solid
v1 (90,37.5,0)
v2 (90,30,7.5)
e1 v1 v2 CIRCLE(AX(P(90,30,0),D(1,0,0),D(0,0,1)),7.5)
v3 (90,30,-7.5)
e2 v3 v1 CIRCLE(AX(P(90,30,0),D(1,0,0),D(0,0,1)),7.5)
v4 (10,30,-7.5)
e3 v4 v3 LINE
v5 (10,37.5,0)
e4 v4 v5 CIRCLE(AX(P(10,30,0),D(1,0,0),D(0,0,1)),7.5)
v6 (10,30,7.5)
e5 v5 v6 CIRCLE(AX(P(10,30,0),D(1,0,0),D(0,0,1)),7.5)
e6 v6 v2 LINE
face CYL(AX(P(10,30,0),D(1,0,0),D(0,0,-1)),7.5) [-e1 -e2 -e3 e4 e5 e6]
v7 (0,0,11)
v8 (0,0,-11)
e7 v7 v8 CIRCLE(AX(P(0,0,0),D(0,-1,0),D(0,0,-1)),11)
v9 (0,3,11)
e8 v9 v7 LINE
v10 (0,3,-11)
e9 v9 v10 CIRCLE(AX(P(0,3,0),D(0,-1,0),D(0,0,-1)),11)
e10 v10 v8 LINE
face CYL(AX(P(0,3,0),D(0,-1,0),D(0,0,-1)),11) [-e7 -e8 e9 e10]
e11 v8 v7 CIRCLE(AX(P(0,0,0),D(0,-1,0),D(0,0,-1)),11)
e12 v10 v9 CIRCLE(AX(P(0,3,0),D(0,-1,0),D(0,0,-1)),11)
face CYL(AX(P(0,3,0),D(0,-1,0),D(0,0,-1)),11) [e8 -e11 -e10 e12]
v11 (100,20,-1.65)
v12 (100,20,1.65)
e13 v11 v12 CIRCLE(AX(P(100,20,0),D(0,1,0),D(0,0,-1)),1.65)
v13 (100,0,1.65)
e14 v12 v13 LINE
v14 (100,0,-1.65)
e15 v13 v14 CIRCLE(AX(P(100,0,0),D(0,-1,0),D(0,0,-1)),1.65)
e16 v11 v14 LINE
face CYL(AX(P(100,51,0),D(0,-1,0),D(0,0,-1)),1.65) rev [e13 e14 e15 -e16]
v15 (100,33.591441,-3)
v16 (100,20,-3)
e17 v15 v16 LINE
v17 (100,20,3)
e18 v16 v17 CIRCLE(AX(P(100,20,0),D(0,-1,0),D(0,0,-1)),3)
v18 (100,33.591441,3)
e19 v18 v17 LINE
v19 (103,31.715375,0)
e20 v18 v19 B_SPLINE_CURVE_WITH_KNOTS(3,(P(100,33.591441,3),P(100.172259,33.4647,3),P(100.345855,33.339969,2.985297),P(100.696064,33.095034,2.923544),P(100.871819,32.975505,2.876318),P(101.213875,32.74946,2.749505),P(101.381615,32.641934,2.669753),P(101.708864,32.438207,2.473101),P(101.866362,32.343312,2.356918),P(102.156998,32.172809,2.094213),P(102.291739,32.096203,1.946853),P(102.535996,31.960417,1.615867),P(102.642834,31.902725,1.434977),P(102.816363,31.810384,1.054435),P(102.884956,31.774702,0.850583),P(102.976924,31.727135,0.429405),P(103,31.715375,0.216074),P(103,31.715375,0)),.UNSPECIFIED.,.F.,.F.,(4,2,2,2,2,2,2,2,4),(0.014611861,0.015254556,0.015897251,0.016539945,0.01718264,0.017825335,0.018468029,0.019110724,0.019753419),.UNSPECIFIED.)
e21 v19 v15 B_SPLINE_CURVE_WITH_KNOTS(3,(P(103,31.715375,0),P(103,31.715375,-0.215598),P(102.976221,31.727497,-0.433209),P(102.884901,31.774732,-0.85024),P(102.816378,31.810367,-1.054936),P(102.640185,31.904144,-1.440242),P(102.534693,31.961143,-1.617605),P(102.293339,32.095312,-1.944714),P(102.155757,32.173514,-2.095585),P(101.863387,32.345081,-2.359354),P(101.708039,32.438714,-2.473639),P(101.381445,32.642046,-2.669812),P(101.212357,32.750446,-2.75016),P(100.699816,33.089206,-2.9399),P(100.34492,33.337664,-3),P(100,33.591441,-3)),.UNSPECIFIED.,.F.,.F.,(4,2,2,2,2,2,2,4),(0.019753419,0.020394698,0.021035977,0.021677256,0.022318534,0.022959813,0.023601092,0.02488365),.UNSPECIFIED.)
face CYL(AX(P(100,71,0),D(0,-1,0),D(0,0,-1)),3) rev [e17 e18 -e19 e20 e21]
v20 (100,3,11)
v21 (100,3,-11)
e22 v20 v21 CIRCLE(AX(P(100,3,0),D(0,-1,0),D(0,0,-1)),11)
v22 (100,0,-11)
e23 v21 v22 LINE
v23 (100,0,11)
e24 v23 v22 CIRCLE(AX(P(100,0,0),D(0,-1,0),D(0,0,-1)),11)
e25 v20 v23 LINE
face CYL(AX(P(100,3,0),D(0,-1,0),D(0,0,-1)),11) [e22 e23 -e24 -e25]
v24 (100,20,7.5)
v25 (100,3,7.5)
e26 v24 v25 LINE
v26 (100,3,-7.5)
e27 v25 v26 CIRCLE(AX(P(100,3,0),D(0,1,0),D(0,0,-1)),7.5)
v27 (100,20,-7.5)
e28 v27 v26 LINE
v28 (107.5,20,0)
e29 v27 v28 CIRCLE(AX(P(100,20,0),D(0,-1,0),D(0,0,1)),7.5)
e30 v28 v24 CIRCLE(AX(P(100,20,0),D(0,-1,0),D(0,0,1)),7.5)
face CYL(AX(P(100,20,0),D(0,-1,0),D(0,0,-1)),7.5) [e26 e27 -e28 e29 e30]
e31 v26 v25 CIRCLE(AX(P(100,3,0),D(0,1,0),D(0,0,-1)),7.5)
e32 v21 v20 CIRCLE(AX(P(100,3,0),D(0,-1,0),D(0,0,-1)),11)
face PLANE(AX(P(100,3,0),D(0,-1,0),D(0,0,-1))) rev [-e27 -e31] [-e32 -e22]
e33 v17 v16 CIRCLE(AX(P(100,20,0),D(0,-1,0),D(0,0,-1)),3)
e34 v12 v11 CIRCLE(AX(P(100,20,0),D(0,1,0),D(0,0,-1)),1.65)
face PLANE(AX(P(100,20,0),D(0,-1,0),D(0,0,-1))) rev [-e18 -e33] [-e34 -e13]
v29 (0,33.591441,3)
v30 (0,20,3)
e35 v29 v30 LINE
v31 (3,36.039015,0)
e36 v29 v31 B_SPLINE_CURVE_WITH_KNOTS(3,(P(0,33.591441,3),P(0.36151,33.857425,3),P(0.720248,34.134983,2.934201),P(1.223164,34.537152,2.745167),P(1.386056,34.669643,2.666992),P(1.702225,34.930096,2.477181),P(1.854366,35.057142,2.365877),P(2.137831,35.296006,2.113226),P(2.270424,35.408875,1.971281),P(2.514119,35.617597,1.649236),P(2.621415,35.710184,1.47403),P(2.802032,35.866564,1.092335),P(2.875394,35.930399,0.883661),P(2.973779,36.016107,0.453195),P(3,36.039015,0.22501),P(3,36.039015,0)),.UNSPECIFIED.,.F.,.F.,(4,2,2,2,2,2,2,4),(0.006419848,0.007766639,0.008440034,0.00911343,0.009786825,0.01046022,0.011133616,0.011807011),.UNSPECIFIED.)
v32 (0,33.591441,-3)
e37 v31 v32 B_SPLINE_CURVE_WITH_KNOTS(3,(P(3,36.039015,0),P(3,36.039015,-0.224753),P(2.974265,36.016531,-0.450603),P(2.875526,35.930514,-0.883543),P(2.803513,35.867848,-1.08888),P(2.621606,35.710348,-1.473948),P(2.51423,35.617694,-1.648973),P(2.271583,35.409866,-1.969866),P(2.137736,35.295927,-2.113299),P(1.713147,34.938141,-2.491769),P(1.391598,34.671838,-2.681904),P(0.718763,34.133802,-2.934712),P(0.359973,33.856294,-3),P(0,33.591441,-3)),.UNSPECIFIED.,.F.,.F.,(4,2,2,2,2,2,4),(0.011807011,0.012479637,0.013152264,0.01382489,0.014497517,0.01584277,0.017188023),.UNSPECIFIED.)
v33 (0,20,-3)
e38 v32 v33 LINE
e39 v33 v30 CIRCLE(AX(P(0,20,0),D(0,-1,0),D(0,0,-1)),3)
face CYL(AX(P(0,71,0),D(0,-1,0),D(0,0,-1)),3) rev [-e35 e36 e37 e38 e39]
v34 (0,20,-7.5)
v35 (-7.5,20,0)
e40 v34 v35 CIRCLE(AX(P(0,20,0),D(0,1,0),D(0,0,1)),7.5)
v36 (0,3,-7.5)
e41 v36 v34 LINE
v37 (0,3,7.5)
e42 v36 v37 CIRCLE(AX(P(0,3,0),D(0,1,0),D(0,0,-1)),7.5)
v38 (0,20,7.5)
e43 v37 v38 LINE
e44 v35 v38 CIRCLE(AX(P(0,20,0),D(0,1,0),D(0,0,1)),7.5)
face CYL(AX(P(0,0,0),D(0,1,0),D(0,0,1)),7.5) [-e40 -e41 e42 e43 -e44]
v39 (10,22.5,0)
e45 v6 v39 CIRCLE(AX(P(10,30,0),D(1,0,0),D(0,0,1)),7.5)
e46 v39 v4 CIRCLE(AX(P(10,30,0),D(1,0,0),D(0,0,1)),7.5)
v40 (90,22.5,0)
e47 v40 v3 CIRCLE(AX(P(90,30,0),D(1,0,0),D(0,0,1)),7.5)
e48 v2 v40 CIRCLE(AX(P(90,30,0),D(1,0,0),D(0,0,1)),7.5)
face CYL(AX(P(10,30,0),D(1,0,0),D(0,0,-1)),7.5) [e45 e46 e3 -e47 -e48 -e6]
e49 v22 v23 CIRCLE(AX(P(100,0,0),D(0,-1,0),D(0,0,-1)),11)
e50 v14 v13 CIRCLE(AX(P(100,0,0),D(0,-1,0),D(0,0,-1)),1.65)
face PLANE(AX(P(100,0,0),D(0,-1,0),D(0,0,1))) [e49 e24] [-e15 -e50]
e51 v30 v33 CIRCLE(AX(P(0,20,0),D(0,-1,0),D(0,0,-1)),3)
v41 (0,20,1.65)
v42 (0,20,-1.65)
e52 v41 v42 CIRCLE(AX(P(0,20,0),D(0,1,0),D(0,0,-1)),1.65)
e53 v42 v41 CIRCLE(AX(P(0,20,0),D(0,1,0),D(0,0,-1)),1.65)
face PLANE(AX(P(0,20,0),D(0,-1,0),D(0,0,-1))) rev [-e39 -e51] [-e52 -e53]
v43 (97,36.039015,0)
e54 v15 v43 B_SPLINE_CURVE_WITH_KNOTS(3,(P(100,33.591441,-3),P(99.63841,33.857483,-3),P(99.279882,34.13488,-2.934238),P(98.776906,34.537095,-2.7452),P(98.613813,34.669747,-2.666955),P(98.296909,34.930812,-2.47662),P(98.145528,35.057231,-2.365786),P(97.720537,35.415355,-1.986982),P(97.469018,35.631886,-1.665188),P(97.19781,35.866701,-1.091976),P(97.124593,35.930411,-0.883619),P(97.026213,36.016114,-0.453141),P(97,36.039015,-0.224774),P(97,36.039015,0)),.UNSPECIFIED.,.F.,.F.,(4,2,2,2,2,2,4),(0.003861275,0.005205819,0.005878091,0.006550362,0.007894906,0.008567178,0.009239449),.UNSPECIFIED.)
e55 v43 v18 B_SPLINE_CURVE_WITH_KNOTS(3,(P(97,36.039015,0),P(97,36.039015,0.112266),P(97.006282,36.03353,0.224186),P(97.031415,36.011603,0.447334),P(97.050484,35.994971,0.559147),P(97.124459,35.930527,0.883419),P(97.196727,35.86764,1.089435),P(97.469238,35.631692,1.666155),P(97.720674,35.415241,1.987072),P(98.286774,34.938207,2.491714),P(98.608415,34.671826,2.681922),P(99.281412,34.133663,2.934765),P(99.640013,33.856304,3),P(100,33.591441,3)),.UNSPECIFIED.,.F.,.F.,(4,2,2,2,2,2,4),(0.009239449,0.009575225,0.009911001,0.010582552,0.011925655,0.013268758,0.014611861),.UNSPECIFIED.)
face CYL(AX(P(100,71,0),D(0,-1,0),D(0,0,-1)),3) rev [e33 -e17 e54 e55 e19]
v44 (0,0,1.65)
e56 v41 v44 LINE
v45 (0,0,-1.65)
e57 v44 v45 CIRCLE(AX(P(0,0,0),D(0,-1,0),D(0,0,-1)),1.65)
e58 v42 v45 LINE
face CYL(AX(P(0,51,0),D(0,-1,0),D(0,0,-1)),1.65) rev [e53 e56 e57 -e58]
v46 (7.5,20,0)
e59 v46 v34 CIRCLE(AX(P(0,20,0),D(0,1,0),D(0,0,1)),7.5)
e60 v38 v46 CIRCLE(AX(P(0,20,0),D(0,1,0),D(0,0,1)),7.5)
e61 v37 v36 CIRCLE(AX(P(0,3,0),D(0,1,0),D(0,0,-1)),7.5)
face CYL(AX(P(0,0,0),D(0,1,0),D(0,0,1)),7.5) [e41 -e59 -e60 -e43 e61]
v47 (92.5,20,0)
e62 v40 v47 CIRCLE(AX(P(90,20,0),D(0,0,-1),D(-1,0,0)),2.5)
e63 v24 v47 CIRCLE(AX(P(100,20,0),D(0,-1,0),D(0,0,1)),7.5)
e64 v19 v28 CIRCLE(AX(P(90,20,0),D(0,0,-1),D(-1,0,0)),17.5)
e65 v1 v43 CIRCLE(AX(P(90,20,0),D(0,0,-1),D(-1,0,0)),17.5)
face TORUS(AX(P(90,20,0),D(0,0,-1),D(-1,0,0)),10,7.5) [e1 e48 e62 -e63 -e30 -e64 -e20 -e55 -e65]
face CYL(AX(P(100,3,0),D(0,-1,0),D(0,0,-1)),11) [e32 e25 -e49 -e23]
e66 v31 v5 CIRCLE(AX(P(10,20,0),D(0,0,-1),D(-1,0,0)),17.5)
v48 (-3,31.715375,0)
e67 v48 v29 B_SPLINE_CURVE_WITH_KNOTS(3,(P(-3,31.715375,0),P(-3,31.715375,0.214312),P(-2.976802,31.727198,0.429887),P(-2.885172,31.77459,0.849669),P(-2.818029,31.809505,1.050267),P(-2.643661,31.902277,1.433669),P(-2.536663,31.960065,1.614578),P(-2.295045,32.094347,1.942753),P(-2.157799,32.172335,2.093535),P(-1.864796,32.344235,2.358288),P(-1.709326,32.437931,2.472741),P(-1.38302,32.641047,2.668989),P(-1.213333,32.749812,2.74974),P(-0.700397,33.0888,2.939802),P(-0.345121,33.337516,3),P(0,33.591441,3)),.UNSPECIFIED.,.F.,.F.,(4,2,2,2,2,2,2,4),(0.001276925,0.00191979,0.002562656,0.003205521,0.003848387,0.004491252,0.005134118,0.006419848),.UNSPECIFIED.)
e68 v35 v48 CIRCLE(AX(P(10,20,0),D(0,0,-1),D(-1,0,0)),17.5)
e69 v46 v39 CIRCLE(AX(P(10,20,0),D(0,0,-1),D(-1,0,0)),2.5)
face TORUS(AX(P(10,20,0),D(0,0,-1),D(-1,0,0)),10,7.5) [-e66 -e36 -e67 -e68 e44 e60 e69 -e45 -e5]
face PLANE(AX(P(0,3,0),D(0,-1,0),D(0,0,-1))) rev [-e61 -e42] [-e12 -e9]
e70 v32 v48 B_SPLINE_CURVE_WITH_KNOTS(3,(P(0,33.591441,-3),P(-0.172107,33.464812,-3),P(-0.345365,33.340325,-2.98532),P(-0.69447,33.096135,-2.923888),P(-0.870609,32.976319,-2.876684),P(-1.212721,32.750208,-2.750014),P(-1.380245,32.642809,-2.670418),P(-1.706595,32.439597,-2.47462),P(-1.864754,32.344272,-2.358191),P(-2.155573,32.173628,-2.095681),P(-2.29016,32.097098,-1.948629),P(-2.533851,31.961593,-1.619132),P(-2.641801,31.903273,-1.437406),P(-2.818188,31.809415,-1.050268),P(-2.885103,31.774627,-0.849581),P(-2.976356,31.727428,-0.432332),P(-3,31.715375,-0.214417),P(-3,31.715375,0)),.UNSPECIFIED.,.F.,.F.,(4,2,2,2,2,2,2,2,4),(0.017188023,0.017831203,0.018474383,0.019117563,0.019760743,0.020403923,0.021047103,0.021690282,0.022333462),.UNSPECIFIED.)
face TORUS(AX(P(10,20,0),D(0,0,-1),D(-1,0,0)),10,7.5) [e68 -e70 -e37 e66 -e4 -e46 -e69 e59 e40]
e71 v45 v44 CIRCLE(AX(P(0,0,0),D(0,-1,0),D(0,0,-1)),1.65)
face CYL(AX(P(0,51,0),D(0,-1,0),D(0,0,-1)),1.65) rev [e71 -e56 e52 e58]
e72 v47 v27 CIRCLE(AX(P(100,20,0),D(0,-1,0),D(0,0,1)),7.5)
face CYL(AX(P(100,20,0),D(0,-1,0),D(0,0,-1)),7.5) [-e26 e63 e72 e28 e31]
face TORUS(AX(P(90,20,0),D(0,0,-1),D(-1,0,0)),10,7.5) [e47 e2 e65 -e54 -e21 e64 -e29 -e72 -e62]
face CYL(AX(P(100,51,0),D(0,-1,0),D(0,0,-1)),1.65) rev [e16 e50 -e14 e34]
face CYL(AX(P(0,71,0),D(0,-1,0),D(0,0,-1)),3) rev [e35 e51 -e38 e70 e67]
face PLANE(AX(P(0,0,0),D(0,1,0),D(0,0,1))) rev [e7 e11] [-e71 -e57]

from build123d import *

# Parameters (mm, degrees)
SKETCH_2_R          = 7.5
SKETCH_3_R          = 11
EXTRUDE_1_DEPTH     = 3
SKETCH_4_R          = 1.65
CUT_EXTRUDE_1_DEPTH = 51
CUT_EXTRUDE_START   = -20
SKETCH_5_R          = 3
CUT_EXTRUDE_2_DEPTH = 51


with BuildPart() as part:
    # 扫描1: sweep along a path in 草图1
    with BuildLine(Plane.XY) as sweep_1_path:
        Line((0, 0), (0, 20))
        ThreePointArc((0, 20), (2.928932188, 27.071067812), (10, 30))
        Line((10, 30), (90, 30))
        ThreePointArc((90, 30), (97.071067812, 27.071067812), (100, 20))
        Line((100, 20), (100, 0))
    # 草图2 → 扫描1 (sweep)
    with BuildSketch(Plane(origin=(0, 0, 0), x_dir=(1, 0, 0), z_dir=(0, 1, 0))):
        Circle(SKETCH_2_R)
    sweep(path=sweep_1_path.line)

    # 草图3 → 凸台-拉伸1 (add)
    with BuildSketch(Plane.XZ):
        with Locations(Location((0, 0, 0), (0, 0, 270))):
            Circle(SKETCH_3_R)
        with Locations(Location((100, 0, 0), (0, 0, 270))):
            Circle(SKETCH_3_R)
    extrude(amount=-EXTRUDE_1_DEPTH)

    # 草图4 → 切除-拉伸1 (cut)
    with BuildSketch(Plane.XZ):
        with Locations(Location((0, 0, 0), (0, 0, 270))):
            Circle(SKETCH_4_R)
        with Locations(Location((100, 0, 0), (0, 0, 270))):
            Circle(SKETCH_4_R)
    extrude(amount=-CUT_EXTRUDE_1_DEPTH, mode=Mode.SUBTRACT)

    # 草图5 → 切除-拉伸2 (cut)
    with BuildSketch(Plane.XZ.offset(CUT_EXTRUDE_START)):
        with Locations(Location((0, 0, 0), (0, 0, 270))):
            Circle(SKETCH_5_R)
        with Locations(Location((100, 0, 0), (0, 0, 270))):
            Circle(SKETCH_5_R)
    extrude(amount=-CUT_EXTRUDE_2_DEPTH, mode=Mode.SUBTRACT)


solid = part.part
